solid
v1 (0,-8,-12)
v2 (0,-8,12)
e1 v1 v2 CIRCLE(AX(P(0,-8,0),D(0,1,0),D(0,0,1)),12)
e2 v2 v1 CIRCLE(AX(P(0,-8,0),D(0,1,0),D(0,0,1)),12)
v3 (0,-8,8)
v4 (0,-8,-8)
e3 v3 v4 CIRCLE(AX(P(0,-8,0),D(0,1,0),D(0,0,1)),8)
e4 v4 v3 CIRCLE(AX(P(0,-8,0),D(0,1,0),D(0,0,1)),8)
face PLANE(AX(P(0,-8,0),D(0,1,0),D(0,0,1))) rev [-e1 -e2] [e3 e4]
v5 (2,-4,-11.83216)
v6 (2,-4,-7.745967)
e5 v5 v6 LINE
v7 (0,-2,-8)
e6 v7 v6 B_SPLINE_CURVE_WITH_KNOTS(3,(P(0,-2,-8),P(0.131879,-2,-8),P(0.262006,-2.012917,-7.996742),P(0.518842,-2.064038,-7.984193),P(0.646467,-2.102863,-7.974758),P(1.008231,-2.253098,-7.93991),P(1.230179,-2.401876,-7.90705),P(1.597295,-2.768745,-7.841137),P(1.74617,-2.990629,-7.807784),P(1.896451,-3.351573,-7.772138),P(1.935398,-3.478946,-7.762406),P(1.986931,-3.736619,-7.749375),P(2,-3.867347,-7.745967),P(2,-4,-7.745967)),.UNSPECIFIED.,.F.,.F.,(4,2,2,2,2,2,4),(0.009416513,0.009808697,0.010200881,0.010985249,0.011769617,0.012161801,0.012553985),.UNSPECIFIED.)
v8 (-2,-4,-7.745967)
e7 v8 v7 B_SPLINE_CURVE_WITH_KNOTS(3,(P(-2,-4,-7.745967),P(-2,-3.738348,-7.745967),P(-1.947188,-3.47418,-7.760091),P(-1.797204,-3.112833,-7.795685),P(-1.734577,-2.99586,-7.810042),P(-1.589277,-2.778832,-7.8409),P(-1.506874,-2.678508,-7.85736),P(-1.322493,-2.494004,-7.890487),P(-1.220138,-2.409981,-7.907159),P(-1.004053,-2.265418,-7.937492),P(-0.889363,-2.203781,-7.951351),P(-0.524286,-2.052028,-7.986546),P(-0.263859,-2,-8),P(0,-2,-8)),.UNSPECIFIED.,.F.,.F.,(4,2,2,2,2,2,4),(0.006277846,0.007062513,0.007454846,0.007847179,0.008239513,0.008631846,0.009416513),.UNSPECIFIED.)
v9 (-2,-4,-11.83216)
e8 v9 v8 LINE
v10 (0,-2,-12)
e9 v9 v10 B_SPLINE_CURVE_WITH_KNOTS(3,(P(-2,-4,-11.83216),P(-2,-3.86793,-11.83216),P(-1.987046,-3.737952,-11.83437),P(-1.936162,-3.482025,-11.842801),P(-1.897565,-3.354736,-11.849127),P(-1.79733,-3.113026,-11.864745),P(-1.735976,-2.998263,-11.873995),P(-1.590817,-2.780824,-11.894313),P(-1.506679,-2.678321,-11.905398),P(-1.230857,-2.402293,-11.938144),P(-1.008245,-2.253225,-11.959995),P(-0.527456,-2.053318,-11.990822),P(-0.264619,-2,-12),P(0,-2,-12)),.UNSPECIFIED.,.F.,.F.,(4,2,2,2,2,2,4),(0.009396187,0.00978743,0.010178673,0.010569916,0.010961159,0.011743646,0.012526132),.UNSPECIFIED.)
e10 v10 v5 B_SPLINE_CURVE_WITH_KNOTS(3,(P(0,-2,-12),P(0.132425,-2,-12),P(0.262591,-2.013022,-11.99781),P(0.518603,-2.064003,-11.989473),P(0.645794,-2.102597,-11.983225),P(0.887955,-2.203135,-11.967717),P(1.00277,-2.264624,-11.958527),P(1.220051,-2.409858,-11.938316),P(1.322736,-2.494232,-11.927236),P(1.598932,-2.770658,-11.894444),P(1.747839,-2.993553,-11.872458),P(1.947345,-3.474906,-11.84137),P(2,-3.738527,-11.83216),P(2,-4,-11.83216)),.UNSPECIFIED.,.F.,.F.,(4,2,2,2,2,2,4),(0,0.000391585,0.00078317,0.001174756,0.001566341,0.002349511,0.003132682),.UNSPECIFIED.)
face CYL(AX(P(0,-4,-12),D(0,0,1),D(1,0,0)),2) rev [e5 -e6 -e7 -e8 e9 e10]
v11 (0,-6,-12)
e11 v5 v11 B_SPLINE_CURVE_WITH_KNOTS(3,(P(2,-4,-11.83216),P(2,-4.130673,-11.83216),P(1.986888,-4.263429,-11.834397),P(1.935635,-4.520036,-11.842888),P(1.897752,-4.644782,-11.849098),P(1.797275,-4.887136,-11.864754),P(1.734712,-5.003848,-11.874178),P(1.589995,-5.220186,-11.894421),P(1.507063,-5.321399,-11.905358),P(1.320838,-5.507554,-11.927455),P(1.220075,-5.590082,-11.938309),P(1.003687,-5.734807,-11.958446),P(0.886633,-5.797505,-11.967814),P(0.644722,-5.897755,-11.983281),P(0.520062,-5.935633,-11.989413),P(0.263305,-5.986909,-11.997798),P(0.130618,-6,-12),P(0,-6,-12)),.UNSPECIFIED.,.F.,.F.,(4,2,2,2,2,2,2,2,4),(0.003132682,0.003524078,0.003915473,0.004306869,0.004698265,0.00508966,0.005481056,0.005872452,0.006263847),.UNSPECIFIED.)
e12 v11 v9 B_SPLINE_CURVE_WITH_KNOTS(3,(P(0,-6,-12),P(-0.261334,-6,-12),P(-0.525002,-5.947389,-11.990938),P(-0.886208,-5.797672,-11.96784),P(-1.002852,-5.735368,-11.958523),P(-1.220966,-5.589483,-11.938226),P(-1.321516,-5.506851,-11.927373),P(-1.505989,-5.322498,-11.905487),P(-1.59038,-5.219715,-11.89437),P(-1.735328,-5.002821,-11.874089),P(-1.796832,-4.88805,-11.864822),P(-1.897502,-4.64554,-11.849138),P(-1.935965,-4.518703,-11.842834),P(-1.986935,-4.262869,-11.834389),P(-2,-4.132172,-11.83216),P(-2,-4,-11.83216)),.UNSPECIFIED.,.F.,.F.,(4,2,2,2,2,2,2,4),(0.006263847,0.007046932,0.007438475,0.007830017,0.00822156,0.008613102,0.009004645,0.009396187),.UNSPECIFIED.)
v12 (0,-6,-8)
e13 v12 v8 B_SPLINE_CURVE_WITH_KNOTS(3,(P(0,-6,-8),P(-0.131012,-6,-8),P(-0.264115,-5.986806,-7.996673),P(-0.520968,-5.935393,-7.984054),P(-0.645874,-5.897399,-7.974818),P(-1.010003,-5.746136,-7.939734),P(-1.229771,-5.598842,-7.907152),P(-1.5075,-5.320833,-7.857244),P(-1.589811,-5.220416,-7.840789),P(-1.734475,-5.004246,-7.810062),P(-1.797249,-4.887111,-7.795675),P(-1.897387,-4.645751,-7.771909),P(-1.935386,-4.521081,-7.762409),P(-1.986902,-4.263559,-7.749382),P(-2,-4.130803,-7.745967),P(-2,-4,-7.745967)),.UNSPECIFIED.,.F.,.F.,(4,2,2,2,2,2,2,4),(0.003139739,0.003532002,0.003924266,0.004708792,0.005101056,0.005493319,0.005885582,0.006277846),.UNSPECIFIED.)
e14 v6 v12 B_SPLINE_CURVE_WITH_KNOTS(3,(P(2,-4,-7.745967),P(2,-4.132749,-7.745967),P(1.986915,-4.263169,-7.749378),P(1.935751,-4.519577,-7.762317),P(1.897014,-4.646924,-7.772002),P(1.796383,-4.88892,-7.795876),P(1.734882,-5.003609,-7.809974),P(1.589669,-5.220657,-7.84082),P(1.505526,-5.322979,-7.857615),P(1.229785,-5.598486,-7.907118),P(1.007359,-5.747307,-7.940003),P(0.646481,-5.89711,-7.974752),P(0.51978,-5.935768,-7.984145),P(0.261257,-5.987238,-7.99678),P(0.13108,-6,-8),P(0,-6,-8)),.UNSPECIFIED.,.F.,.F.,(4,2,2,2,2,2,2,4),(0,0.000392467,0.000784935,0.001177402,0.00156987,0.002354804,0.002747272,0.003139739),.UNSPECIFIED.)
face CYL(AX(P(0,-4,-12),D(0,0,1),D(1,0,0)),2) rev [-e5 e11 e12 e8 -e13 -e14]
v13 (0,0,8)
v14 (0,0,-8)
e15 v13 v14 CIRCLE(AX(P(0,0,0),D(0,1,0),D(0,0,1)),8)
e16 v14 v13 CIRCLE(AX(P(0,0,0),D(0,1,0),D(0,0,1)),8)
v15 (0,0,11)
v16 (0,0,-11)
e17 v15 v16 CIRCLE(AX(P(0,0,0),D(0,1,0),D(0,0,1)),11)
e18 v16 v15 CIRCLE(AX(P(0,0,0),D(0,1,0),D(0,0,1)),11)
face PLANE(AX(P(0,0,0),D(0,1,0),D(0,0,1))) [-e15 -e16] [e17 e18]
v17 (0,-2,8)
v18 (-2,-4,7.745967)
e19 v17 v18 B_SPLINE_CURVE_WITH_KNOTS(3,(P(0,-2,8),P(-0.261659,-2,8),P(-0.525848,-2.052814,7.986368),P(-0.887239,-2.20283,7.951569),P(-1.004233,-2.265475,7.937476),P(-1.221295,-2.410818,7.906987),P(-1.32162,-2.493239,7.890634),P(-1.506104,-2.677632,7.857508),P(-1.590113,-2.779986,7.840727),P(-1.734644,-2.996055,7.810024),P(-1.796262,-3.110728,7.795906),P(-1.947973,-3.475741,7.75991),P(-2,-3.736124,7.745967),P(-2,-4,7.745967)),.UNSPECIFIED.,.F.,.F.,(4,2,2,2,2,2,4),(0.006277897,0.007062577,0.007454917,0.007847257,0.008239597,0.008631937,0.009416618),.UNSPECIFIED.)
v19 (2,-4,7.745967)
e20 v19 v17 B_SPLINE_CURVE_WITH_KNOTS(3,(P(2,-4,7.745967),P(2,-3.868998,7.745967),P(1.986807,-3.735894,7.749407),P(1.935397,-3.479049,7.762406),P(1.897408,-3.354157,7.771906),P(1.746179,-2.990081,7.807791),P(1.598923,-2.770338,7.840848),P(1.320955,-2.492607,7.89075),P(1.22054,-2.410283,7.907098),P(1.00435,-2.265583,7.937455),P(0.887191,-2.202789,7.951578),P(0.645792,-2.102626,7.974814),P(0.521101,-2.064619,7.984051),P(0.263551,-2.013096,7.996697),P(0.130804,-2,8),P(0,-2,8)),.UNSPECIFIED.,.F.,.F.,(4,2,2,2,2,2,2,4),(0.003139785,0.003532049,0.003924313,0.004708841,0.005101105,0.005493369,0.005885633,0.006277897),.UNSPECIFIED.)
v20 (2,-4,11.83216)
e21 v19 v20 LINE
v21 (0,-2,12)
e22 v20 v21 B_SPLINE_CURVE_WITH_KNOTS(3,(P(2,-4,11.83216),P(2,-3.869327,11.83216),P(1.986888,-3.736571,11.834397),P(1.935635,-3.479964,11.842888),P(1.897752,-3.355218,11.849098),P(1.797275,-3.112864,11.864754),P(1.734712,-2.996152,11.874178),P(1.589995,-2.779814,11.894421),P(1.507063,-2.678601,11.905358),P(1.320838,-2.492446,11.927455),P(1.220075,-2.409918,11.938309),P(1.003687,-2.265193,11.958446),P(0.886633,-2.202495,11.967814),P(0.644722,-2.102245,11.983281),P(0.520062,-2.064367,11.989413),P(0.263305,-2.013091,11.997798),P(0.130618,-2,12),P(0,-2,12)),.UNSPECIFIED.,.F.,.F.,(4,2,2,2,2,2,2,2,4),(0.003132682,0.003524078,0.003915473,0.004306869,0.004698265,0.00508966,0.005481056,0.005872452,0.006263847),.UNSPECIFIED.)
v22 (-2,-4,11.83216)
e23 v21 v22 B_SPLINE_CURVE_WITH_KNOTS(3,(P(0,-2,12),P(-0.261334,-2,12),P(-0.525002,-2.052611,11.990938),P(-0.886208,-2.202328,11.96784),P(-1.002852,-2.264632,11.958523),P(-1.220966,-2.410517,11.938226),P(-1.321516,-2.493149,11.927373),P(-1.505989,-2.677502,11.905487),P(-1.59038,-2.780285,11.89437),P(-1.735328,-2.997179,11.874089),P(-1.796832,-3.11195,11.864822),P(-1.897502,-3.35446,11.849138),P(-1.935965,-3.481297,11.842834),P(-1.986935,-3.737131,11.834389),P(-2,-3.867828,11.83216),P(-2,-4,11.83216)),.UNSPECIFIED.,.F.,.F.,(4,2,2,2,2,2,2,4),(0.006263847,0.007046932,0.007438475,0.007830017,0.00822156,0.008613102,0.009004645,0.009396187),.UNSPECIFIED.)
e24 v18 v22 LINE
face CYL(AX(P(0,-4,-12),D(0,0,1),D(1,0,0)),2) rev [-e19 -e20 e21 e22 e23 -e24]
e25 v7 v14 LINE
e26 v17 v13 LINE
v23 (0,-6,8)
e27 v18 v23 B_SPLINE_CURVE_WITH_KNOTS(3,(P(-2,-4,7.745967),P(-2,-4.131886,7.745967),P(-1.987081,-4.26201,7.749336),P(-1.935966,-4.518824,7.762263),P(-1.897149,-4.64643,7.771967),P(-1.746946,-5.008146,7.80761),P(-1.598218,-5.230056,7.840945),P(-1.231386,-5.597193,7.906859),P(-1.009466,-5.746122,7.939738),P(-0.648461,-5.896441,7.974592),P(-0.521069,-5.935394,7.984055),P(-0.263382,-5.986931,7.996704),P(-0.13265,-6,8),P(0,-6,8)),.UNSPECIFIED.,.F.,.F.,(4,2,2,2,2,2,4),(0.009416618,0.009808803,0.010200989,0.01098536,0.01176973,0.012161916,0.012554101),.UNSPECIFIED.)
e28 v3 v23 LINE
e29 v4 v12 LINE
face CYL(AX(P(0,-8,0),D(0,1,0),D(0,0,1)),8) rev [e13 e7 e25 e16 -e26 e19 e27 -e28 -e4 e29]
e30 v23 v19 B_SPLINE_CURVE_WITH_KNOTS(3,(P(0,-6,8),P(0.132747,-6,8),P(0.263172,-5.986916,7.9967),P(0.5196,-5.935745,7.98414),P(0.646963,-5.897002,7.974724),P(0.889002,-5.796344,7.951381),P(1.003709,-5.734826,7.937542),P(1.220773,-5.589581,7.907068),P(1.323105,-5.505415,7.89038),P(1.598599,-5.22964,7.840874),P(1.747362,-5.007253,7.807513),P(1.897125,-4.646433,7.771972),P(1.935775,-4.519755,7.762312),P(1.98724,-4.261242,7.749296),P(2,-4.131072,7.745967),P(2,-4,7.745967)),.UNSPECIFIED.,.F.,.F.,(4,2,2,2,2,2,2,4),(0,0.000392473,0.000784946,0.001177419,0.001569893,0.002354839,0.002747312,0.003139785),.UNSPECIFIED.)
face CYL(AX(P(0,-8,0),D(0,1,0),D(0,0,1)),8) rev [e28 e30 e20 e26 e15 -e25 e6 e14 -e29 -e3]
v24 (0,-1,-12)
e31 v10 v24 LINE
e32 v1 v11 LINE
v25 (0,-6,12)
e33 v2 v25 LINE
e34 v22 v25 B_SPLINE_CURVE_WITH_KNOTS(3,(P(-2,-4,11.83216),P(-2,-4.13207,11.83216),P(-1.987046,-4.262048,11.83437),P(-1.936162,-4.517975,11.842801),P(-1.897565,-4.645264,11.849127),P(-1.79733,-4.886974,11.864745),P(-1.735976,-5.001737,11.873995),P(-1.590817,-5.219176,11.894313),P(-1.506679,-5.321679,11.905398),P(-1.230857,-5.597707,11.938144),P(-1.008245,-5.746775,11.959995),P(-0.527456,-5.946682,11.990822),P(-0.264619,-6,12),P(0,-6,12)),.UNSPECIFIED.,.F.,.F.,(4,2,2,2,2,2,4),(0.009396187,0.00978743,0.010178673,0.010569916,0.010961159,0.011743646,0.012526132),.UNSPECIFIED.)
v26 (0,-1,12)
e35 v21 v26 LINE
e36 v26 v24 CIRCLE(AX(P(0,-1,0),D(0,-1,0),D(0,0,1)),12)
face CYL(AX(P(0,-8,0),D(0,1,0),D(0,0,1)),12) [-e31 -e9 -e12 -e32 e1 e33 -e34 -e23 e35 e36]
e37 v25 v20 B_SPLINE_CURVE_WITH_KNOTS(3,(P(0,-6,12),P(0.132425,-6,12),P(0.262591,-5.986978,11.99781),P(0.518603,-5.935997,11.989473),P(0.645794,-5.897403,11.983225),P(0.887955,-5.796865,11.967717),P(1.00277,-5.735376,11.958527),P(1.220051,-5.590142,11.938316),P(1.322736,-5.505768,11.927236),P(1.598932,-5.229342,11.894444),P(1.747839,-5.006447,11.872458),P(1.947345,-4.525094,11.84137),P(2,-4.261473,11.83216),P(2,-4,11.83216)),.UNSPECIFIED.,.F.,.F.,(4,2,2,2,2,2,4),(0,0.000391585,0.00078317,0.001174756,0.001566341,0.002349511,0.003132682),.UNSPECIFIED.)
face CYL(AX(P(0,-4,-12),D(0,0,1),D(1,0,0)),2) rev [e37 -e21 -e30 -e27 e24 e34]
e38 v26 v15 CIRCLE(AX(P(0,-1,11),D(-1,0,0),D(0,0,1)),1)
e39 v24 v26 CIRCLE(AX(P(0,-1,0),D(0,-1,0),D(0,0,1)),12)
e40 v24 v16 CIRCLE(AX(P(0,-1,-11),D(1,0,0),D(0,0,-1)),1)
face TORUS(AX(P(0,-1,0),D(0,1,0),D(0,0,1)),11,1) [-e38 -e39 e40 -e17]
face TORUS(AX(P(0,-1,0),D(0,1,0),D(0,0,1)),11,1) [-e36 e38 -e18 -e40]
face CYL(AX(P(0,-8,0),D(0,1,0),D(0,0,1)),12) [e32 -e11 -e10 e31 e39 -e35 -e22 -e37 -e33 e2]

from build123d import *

# Parameters (mm, degrees)
SKETCH1_R               = 12
SKETCH1_R_2             = 8
BOSS_EXTRUDE1_DEPTH     = 8
CUT_EXTRUDE1_DEPTH      = 19.761663039
CUT_EXTRUDE1_DEPTH_BACK = 19.761663039
SKETCH2_R               = 2
FILLET1_R               = 1


with BuildPart() as part:
    # Sketch1 → Boss-Extrude1 (new body)
    with BuildSketch(Plane(origin=(0, 0, 0), x_dir=(1, 0, 0), z_dir=(0, 1, 0))):
        with Locations(Location((0, 0, 0), (0, 0, 270))):
            Circle(SKETCH1_R)
        with Locations(Location((0, 0, 0), (0, 0, 270))):
            Circle(SKETCH1_R_2, mode=Mode.SUBTRACT)
    extrude(amount=-BOSS_EXTRUDE1_DEPTH)

    # Sketch2 → Cut-Extrude1 (cut, two sides: drawn at the far end of the back side and taken through both)
    with BuildSketch(Plane.XY.offset(-CUT_EXTRUDE1_DEPTH_BACK)):
        with Locations((0, -4)):
            Circle(SKETCH2_R)
    extrude(amount=CUT_EXTRUDE1_DEPTH + CUT_EXTRUDE1_DEPTH_BACK, mode=Mode.SUBTRACT)

    # Fillet1
    fillet1_edges = [part.edges().sort_by_distance(p)[0] for p in [
        (0, 0, -12),
    ]]
    fillet(fillet1_edges, radius=FILLET1_R)


solid = part.part
